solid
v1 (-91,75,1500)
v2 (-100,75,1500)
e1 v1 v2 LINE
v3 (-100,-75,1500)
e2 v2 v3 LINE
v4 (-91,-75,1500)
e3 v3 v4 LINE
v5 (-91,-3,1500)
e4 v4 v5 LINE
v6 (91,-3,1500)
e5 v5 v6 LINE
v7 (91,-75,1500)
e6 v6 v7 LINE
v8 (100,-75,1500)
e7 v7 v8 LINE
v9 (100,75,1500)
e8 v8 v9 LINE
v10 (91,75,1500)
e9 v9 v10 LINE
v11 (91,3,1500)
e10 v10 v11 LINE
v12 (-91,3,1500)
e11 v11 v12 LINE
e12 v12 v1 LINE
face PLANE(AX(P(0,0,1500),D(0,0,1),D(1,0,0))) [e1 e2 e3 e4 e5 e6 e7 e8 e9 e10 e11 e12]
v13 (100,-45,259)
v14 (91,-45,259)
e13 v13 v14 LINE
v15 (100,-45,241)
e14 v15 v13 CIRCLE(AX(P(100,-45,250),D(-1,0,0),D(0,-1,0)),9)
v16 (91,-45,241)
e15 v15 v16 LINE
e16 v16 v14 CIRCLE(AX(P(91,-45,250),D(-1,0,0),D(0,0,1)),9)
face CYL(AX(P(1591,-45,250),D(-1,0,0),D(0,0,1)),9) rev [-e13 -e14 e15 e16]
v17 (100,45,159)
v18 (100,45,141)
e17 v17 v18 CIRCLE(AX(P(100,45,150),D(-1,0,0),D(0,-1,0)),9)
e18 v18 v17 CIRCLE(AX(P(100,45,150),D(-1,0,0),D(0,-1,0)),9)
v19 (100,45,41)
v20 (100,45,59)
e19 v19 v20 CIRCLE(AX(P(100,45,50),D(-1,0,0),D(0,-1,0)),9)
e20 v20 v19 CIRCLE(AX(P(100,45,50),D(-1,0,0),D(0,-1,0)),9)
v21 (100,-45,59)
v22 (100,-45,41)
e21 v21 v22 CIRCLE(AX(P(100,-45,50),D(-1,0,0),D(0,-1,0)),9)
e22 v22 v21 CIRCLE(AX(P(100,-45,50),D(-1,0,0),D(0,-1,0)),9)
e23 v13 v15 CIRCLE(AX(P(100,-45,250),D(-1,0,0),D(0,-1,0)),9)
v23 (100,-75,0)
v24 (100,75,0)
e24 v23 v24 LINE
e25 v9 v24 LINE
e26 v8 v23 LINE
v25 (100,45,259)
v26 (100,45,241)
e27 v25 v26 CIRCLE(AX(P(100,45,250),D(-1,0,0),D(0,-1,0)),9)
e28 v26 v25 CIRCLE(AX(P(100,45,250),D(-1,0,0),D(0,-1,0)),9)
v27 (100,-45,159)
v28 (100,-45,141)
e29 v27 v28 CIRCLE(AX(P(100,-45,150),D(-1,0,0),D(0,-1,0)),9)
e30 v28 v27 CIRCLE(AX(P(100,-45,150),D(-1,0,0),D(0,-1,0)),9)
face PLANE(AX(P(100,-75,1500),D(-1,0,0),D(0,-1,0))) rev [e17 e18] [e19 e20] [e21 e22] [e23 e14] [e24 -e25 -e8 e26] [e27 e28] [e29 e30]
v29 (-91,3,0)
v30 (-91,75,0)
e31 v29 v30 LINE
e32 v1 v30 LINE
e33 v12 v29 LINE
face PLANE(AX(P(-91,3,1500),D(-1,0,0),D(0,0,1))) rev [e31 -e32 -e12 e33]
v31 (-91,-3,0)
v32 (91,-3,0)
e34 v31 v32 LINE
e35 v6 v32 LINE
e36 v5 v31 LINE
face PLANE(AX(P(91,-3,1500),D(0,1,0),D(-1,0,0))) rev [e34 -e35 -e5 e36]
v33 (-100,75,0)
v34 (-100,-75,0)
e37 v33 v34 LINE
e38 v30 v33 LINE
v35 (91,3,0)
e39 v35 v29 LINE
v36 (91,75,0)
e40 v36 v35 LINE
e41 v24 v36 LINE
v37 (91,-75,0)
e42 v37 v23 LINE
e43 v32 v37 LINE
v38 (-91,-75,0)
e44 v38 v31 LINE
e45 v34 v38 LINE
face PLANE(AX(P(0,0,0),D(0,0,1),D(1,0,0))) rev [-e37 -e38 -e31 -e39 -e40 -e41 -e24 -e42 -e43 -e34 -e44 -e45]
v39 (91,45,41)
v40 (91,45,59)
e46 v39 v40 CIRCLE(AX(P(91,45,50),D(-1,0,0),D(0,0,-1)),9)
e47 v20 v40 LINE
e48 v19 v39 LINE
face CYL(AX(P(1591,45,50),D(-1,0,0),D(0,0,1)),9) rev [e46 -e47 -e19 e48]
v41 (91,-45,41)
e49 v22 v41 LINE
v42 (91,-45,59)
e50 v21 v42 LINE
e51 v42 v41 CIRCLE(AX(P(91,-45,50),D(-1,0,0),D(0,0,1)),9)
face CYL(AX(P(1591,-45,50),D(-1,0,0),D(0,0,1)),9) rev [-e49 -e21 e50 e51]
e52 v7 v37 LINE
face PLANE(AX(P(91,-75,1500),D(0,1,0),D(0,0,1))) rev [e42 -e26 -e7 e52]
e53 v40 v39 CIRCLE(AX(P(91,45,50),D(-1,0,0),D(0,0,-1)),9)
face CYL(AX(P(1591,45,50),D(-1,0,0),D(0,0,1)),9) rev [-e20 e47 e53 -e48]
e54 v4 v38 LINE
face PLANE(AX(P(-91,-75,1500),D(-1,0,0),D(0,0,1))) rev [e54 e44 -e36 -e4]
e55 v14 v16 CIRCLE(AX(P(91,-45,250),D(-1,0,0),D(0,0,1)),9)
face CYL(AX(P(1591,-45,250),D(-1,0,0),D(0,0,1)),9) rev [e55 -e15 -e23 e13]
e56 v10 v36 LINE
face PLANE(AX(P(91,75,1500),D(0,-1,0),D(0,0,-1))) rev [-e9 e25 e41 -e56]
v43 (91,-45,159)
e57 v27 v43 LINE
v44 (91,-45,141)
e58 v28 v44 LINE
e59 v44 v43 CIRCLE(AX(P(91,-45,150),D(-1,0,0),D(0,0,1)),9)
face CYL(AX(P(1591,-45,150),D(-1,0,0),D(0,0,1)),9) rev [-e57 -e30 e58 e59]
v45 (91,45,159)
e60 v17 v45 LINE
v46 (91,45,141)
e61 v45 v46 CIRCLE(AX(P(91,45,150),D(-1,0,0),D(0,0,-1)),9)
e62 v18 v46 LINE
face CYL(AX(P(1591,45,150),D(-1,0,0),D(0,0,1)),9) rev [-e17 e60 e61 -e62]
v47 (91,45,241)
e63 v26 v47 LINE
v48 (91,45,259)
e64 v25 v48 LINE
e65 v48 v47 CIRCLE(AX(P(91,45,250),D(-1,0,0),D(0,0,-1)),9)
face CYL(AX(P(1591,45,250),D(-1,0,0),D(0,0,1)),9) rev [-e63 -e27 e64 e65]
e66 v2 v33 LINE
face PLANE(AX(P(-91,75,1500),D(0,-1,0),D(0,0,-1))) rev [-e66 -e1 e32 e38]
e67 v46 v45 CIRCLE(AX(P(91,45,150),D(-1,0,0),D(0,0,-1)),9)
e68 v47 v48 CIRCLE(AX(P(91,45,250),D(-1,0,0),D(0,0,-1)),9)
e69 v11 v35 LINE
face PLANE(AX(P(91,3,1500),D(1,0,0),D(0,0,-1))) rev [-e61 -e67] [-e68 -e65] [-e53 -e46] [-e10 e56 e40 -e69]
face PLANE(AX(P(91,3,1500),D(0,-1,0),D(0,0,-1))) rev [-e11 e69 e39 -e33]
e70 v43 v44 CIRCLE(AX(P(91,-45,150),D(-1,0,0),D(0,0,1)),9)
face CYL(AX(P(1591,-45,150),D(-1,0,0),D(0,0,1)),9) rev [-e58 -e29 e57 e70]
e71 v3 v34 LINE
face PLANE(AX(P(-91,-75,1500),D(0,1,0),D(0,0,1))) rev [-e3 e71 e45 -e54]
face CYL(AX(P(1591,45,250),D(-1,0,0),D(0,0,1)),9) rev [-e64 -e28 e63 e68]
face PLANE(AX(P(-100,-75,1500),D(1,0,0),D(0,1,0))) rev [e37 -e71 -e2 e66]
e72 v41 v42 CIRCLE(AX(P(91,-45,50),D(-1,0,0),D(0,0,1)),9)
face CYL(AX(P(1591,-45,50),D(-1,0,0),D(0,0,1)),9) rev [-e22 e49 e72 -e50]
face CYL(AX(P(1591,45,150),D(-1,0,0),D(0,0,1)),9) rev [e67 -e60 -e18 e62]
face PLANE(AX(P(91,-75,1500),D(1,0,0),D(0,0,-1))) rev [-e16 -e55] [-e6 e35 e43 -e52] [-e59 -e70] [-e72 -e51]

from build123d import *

# Parameters (mm, degrees)
BOSS_EXTRUDE1_DEPTH = 1500
SKETCH2_R           = 9
CUT_EXTRUDE1_DEPTH  = 1500


with BuildPart() as part:
    # Sketch1 → Boss-Extrude1 (new body)
    with BuildSketch(Plane.XY):
        Polygon((-91, -75), (-100, -75), (-100, 75), (-91, 75), (-91, 3), (91, 3), (91, 75), (100, 75), (100, -75), (91, -75), (91, -3), (-91, -3), align=None)
    extrude(amount=BOSS_EXTRUDE1_DEPTH)

    # Sketch2 → Cut-Extrude1 (cut)
    with BuildSketch(Plane.ZY.offset(-91)):
        with Locations((50, -45)):
            Circle(SKETCH2_R)
        with Locations((150, -45)):
            Circle(SKETCH2_R)
        with Locations((250, -45)):
            Circle(SKETCH2_R)
        with Locations(Location((250, 45, 0), (0, 0, 270))):
            Circle(SKETCH2_R)
        with Locations(Location((150, 45, 0), (0, 0, 270))):
            Circle(SKETCH2_R)
        with Locations(Location((50, 45, 0), (0, 0, 270))):
            Circle(SKETCH2_R)
    extrude(amount=-CUT_EXTRUDE1_DEPTH, mode=Mode.SUBTRACT)


solid = part.part
